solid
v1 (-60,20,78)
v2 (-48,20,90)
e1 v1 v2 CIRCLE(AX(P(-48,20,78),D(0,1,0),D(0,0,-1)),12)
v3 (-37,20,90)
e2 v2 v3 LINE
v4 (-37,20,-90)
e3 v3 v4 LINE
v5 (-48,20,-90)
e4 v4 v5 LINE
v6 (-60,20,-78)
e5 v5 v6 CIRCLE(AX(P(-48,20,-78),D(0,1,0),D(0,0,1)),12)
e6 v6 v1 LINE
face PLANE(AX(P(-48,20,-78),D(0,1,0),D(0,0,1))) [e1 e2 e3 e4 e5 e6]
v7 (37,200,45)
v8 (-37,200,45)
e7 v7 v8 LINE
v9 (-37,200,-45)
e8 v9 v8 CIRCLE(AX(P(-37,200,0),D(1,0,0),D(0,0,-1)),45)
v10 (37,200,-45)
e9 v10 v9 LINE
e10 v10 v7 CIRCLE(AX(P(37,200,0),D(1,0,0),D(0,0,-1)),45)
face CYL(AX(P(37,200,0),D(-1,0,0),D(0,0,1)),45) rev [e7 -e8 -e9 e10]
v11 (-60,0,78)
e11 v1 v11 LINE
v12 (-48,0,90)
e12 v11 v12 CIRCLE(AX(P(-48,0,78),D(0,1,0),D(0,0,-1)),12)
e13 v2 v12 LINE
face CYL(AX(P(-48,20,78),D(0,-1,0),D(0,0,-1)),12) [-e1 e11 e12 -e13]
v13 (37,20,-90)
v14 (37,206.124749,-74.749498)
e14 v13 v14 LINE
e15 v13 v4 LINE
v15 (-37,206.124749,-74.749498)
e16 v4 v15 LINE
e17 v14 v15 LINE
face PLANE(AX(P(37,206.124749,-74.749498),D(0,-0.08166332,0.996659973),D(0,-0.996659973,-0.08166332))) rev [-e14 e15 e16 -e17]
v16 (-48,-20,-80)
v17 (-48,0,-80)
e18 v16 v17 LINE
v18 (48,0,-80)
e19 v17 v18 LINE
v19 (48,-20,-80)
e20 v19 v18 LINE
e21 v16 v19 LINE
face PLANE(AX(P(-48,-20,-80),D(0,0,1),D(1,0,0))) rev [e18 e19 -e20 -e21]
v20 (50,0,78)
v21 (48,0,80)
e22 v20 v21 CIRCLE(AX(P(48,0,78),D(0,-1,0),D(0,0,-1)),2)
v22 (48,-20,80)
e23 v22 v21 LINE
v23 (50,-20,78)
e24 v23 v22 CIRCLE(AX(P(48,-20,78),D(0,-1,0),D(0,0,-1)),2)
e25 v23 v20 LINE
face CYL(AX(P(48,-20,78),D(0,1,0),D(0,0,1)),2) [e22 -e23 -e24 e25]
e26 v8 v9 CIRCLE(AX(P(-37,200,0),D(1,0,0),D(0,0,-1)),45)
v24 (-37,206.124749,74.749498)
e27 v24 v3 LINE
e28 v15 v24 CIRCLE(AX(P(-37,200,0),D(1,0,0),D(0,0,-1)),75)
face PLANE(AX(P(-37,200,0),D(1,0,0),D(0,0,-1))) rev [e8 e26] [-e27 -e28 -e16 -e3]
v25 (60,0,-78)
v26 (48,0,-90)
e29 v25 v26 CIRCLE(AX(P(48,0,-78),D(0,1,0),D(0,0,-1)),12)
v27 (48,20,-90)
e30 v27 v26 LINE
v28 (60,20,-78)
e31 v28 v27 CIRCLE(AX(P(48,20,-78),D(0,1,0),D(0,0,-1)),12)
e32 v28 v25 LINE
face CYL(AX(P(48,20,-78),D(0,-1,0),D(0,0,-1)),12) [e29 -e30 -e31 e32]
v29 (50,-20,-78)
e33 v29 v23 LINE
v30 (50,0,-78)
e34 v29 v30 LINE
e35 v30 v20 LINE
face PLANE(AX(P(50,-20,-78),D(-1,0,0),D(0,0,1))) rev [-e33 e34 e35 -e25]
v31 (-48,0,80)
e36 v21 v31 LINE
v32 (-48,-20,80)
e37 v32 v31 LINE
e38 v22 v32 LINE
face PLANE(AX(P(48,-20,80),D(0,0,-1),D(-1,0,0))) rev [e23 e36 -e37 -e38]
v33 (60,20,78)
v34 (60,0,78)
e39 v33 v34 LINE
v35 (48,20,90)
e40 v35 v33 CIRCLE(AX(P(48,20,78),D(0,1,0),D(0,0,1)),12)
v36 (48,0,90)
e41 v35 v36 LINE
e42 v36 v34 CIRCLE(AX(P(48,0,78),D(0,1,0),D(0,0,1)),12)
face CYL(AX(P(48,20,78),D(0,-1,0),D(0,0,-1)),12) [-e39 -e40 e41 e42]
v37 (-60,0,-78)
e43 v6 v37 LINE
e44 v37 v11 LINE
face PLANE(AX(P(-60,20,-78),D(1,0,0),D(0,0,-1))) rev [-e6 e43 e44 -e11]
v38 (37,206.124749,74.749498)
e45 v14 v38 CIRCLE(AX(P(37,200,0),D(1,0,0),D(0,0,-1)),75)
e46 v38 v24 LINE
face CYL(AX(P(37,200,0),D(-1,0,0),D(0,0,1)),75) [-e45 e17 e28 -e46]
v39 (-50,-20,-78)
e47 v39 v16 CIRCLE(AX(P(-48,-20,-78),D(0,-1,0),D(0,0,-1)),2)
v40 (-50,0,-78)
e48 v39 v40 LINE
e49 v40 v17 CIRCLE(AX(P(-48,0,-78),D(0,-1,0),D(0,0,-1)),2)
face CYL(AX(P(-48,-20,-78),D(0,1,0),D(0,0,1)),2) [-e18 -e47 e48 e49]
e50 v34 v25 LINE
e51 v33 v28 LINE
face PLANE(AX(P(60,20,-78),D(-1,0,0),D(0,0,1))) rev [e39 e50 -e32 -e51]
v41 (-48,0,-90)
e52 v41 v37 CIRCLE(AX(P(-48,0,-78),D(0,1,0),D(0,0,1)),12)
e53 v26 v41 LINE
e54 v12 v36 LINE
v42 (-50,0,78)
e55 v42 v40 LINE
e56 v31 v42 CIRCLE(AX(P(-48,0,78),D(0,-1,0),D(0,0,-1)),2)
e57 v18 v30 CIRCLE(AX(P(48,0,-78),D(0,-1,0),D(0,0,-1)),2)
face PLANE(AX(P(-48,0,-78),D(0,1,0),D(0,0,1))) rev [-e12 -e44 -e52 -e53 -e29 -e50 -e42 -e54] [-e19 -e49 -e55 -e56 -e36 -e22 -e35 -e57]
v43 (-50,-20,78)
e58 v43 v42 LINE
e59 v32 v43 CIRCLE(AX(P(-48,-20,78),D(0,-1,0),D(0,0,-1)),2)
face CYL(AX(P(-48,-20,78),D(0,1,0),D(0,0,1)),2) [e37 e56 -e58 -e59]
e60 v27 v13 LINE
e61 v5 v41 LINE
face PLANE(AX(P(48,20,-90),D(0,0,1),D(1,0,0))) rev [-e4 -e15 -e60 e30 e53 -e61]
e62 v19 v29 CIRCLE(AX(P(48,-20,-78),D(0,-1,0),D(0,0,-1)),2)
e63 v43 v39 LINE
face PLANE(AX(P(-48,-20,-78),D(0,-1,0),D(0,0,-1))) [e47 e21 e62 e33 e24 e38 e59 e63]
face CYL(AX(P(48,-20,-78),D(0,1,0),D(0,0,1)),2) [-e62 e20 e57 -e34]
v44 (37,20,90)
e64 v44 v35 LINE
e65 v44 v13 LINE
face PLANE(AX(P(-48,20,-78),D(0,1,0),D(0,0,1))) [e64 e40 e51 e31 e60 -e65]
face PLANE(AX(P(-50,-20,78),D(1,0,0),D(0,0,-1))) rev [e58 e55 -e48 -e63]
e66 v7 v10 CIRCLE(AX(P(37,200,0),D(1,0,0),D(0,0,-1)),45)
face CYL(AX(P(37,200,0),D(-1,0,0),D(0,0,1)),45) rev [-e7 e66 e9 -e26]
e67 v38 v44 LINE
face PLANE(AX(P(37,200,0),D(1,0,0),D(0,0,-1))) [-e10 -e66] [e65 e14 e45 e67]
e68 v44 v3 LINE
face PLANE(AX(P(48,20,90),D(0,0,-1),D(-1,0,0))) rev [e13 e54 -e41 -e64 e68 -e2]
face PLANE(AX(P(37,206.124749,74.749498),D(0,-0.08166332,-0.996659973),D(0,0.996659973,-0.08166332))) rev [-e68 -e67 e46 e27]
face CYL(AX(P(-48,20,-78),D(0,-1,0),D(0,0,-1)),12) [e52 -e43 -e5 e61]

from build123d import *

# Parameters (mm, degrees)
BOSS_EXTRUDE_1_DEPTH = 20
BOSS_EXTRUDE_2_DEPTH = 20
SKETCH_3_R           = 45
BOSS_EXTRUDE_3_DEPTH = 37


with BuildPart() as part:
    # Sketch 1 → Boss-Extrude 1 (new body)
    with BuildSketch(Plane(origin=(0, 0, 0), x_dir=(1, 0, 0), z_dir=(0, 1, 0))):
        with BuildLine():
            Line((48, 90), (-48, 90))
            ThreePointArc((-48, 90), (-56.485281374, 86.485281374), (-60, 78))
            Line((-60, 78), (-60, -78))
            ThreePointArc((-60, -78), (-56.485281374, -86.485281374), (-48, -90))
            Line((-48, -90), (48, -90))
            ThreePointArc((48, -90), (56.485281374, -86.485281374), (60, -78))
            Line((60, -78), (60, 78))
            ThreePointArc((60, 78), (56.485281374, 86.485281374), (48, 90))
        make_face()
    extrude(amount=BOSS_EXTRUDE_1_DEPTH)

    # Sketch 2 → Boss-Extrude 2 (add)
    with BuildSketch(Plane.XZ):
        with BuildLine():
            Line((-48, -80), (48, -80))
            ThreePointArc((48, -80), (49.414213562, -79.414213562), (50, -78))
            Line((50, -78), (50, 78))
            ThreePointArc((50, 78), (49.414213562, 79.414213562), (48, 80))
            Line((48, 80), (-48, 80))
            ThreePointArc((-48, 80), (-49.414213562, 79.414213562), (-50, 78))
            Line((-50, 78), (-50, -78))
            ThreePointArc((-50, -78), (-49.414213562, -79.414213562), (-48, -80))
        make_face()
    extrude(amount=BOSS_EXTRUDE_2_DEPTH)

    # Sketch 3 → Boss-Extrude 3 (add, symmetric)
    with BuildSketch(Plane(origin=(0, 0, 0), x_dir=(0, 0, -1), z_dir=(1, 0, 0))):
        with BuildLine():
            Line((-74.74949799, 206.124748995), (-90, 20))
            Line((-90, 20), (90, 20))
            Line((90, 20), (74.74949799, 206.124748995))
            ThreePointArc((74.74949799, 206.124748995), (0, 275), (-74.74949799, 206.124748995))
        make_face()
        with Locations((0, 200)):
            Circle(SKETCH_3_R, mode=Mode.SUBTRACT)
    extrude(amount=BOSS_EXTRUDE_3_DEPTH, both=True)


solid = part.part
